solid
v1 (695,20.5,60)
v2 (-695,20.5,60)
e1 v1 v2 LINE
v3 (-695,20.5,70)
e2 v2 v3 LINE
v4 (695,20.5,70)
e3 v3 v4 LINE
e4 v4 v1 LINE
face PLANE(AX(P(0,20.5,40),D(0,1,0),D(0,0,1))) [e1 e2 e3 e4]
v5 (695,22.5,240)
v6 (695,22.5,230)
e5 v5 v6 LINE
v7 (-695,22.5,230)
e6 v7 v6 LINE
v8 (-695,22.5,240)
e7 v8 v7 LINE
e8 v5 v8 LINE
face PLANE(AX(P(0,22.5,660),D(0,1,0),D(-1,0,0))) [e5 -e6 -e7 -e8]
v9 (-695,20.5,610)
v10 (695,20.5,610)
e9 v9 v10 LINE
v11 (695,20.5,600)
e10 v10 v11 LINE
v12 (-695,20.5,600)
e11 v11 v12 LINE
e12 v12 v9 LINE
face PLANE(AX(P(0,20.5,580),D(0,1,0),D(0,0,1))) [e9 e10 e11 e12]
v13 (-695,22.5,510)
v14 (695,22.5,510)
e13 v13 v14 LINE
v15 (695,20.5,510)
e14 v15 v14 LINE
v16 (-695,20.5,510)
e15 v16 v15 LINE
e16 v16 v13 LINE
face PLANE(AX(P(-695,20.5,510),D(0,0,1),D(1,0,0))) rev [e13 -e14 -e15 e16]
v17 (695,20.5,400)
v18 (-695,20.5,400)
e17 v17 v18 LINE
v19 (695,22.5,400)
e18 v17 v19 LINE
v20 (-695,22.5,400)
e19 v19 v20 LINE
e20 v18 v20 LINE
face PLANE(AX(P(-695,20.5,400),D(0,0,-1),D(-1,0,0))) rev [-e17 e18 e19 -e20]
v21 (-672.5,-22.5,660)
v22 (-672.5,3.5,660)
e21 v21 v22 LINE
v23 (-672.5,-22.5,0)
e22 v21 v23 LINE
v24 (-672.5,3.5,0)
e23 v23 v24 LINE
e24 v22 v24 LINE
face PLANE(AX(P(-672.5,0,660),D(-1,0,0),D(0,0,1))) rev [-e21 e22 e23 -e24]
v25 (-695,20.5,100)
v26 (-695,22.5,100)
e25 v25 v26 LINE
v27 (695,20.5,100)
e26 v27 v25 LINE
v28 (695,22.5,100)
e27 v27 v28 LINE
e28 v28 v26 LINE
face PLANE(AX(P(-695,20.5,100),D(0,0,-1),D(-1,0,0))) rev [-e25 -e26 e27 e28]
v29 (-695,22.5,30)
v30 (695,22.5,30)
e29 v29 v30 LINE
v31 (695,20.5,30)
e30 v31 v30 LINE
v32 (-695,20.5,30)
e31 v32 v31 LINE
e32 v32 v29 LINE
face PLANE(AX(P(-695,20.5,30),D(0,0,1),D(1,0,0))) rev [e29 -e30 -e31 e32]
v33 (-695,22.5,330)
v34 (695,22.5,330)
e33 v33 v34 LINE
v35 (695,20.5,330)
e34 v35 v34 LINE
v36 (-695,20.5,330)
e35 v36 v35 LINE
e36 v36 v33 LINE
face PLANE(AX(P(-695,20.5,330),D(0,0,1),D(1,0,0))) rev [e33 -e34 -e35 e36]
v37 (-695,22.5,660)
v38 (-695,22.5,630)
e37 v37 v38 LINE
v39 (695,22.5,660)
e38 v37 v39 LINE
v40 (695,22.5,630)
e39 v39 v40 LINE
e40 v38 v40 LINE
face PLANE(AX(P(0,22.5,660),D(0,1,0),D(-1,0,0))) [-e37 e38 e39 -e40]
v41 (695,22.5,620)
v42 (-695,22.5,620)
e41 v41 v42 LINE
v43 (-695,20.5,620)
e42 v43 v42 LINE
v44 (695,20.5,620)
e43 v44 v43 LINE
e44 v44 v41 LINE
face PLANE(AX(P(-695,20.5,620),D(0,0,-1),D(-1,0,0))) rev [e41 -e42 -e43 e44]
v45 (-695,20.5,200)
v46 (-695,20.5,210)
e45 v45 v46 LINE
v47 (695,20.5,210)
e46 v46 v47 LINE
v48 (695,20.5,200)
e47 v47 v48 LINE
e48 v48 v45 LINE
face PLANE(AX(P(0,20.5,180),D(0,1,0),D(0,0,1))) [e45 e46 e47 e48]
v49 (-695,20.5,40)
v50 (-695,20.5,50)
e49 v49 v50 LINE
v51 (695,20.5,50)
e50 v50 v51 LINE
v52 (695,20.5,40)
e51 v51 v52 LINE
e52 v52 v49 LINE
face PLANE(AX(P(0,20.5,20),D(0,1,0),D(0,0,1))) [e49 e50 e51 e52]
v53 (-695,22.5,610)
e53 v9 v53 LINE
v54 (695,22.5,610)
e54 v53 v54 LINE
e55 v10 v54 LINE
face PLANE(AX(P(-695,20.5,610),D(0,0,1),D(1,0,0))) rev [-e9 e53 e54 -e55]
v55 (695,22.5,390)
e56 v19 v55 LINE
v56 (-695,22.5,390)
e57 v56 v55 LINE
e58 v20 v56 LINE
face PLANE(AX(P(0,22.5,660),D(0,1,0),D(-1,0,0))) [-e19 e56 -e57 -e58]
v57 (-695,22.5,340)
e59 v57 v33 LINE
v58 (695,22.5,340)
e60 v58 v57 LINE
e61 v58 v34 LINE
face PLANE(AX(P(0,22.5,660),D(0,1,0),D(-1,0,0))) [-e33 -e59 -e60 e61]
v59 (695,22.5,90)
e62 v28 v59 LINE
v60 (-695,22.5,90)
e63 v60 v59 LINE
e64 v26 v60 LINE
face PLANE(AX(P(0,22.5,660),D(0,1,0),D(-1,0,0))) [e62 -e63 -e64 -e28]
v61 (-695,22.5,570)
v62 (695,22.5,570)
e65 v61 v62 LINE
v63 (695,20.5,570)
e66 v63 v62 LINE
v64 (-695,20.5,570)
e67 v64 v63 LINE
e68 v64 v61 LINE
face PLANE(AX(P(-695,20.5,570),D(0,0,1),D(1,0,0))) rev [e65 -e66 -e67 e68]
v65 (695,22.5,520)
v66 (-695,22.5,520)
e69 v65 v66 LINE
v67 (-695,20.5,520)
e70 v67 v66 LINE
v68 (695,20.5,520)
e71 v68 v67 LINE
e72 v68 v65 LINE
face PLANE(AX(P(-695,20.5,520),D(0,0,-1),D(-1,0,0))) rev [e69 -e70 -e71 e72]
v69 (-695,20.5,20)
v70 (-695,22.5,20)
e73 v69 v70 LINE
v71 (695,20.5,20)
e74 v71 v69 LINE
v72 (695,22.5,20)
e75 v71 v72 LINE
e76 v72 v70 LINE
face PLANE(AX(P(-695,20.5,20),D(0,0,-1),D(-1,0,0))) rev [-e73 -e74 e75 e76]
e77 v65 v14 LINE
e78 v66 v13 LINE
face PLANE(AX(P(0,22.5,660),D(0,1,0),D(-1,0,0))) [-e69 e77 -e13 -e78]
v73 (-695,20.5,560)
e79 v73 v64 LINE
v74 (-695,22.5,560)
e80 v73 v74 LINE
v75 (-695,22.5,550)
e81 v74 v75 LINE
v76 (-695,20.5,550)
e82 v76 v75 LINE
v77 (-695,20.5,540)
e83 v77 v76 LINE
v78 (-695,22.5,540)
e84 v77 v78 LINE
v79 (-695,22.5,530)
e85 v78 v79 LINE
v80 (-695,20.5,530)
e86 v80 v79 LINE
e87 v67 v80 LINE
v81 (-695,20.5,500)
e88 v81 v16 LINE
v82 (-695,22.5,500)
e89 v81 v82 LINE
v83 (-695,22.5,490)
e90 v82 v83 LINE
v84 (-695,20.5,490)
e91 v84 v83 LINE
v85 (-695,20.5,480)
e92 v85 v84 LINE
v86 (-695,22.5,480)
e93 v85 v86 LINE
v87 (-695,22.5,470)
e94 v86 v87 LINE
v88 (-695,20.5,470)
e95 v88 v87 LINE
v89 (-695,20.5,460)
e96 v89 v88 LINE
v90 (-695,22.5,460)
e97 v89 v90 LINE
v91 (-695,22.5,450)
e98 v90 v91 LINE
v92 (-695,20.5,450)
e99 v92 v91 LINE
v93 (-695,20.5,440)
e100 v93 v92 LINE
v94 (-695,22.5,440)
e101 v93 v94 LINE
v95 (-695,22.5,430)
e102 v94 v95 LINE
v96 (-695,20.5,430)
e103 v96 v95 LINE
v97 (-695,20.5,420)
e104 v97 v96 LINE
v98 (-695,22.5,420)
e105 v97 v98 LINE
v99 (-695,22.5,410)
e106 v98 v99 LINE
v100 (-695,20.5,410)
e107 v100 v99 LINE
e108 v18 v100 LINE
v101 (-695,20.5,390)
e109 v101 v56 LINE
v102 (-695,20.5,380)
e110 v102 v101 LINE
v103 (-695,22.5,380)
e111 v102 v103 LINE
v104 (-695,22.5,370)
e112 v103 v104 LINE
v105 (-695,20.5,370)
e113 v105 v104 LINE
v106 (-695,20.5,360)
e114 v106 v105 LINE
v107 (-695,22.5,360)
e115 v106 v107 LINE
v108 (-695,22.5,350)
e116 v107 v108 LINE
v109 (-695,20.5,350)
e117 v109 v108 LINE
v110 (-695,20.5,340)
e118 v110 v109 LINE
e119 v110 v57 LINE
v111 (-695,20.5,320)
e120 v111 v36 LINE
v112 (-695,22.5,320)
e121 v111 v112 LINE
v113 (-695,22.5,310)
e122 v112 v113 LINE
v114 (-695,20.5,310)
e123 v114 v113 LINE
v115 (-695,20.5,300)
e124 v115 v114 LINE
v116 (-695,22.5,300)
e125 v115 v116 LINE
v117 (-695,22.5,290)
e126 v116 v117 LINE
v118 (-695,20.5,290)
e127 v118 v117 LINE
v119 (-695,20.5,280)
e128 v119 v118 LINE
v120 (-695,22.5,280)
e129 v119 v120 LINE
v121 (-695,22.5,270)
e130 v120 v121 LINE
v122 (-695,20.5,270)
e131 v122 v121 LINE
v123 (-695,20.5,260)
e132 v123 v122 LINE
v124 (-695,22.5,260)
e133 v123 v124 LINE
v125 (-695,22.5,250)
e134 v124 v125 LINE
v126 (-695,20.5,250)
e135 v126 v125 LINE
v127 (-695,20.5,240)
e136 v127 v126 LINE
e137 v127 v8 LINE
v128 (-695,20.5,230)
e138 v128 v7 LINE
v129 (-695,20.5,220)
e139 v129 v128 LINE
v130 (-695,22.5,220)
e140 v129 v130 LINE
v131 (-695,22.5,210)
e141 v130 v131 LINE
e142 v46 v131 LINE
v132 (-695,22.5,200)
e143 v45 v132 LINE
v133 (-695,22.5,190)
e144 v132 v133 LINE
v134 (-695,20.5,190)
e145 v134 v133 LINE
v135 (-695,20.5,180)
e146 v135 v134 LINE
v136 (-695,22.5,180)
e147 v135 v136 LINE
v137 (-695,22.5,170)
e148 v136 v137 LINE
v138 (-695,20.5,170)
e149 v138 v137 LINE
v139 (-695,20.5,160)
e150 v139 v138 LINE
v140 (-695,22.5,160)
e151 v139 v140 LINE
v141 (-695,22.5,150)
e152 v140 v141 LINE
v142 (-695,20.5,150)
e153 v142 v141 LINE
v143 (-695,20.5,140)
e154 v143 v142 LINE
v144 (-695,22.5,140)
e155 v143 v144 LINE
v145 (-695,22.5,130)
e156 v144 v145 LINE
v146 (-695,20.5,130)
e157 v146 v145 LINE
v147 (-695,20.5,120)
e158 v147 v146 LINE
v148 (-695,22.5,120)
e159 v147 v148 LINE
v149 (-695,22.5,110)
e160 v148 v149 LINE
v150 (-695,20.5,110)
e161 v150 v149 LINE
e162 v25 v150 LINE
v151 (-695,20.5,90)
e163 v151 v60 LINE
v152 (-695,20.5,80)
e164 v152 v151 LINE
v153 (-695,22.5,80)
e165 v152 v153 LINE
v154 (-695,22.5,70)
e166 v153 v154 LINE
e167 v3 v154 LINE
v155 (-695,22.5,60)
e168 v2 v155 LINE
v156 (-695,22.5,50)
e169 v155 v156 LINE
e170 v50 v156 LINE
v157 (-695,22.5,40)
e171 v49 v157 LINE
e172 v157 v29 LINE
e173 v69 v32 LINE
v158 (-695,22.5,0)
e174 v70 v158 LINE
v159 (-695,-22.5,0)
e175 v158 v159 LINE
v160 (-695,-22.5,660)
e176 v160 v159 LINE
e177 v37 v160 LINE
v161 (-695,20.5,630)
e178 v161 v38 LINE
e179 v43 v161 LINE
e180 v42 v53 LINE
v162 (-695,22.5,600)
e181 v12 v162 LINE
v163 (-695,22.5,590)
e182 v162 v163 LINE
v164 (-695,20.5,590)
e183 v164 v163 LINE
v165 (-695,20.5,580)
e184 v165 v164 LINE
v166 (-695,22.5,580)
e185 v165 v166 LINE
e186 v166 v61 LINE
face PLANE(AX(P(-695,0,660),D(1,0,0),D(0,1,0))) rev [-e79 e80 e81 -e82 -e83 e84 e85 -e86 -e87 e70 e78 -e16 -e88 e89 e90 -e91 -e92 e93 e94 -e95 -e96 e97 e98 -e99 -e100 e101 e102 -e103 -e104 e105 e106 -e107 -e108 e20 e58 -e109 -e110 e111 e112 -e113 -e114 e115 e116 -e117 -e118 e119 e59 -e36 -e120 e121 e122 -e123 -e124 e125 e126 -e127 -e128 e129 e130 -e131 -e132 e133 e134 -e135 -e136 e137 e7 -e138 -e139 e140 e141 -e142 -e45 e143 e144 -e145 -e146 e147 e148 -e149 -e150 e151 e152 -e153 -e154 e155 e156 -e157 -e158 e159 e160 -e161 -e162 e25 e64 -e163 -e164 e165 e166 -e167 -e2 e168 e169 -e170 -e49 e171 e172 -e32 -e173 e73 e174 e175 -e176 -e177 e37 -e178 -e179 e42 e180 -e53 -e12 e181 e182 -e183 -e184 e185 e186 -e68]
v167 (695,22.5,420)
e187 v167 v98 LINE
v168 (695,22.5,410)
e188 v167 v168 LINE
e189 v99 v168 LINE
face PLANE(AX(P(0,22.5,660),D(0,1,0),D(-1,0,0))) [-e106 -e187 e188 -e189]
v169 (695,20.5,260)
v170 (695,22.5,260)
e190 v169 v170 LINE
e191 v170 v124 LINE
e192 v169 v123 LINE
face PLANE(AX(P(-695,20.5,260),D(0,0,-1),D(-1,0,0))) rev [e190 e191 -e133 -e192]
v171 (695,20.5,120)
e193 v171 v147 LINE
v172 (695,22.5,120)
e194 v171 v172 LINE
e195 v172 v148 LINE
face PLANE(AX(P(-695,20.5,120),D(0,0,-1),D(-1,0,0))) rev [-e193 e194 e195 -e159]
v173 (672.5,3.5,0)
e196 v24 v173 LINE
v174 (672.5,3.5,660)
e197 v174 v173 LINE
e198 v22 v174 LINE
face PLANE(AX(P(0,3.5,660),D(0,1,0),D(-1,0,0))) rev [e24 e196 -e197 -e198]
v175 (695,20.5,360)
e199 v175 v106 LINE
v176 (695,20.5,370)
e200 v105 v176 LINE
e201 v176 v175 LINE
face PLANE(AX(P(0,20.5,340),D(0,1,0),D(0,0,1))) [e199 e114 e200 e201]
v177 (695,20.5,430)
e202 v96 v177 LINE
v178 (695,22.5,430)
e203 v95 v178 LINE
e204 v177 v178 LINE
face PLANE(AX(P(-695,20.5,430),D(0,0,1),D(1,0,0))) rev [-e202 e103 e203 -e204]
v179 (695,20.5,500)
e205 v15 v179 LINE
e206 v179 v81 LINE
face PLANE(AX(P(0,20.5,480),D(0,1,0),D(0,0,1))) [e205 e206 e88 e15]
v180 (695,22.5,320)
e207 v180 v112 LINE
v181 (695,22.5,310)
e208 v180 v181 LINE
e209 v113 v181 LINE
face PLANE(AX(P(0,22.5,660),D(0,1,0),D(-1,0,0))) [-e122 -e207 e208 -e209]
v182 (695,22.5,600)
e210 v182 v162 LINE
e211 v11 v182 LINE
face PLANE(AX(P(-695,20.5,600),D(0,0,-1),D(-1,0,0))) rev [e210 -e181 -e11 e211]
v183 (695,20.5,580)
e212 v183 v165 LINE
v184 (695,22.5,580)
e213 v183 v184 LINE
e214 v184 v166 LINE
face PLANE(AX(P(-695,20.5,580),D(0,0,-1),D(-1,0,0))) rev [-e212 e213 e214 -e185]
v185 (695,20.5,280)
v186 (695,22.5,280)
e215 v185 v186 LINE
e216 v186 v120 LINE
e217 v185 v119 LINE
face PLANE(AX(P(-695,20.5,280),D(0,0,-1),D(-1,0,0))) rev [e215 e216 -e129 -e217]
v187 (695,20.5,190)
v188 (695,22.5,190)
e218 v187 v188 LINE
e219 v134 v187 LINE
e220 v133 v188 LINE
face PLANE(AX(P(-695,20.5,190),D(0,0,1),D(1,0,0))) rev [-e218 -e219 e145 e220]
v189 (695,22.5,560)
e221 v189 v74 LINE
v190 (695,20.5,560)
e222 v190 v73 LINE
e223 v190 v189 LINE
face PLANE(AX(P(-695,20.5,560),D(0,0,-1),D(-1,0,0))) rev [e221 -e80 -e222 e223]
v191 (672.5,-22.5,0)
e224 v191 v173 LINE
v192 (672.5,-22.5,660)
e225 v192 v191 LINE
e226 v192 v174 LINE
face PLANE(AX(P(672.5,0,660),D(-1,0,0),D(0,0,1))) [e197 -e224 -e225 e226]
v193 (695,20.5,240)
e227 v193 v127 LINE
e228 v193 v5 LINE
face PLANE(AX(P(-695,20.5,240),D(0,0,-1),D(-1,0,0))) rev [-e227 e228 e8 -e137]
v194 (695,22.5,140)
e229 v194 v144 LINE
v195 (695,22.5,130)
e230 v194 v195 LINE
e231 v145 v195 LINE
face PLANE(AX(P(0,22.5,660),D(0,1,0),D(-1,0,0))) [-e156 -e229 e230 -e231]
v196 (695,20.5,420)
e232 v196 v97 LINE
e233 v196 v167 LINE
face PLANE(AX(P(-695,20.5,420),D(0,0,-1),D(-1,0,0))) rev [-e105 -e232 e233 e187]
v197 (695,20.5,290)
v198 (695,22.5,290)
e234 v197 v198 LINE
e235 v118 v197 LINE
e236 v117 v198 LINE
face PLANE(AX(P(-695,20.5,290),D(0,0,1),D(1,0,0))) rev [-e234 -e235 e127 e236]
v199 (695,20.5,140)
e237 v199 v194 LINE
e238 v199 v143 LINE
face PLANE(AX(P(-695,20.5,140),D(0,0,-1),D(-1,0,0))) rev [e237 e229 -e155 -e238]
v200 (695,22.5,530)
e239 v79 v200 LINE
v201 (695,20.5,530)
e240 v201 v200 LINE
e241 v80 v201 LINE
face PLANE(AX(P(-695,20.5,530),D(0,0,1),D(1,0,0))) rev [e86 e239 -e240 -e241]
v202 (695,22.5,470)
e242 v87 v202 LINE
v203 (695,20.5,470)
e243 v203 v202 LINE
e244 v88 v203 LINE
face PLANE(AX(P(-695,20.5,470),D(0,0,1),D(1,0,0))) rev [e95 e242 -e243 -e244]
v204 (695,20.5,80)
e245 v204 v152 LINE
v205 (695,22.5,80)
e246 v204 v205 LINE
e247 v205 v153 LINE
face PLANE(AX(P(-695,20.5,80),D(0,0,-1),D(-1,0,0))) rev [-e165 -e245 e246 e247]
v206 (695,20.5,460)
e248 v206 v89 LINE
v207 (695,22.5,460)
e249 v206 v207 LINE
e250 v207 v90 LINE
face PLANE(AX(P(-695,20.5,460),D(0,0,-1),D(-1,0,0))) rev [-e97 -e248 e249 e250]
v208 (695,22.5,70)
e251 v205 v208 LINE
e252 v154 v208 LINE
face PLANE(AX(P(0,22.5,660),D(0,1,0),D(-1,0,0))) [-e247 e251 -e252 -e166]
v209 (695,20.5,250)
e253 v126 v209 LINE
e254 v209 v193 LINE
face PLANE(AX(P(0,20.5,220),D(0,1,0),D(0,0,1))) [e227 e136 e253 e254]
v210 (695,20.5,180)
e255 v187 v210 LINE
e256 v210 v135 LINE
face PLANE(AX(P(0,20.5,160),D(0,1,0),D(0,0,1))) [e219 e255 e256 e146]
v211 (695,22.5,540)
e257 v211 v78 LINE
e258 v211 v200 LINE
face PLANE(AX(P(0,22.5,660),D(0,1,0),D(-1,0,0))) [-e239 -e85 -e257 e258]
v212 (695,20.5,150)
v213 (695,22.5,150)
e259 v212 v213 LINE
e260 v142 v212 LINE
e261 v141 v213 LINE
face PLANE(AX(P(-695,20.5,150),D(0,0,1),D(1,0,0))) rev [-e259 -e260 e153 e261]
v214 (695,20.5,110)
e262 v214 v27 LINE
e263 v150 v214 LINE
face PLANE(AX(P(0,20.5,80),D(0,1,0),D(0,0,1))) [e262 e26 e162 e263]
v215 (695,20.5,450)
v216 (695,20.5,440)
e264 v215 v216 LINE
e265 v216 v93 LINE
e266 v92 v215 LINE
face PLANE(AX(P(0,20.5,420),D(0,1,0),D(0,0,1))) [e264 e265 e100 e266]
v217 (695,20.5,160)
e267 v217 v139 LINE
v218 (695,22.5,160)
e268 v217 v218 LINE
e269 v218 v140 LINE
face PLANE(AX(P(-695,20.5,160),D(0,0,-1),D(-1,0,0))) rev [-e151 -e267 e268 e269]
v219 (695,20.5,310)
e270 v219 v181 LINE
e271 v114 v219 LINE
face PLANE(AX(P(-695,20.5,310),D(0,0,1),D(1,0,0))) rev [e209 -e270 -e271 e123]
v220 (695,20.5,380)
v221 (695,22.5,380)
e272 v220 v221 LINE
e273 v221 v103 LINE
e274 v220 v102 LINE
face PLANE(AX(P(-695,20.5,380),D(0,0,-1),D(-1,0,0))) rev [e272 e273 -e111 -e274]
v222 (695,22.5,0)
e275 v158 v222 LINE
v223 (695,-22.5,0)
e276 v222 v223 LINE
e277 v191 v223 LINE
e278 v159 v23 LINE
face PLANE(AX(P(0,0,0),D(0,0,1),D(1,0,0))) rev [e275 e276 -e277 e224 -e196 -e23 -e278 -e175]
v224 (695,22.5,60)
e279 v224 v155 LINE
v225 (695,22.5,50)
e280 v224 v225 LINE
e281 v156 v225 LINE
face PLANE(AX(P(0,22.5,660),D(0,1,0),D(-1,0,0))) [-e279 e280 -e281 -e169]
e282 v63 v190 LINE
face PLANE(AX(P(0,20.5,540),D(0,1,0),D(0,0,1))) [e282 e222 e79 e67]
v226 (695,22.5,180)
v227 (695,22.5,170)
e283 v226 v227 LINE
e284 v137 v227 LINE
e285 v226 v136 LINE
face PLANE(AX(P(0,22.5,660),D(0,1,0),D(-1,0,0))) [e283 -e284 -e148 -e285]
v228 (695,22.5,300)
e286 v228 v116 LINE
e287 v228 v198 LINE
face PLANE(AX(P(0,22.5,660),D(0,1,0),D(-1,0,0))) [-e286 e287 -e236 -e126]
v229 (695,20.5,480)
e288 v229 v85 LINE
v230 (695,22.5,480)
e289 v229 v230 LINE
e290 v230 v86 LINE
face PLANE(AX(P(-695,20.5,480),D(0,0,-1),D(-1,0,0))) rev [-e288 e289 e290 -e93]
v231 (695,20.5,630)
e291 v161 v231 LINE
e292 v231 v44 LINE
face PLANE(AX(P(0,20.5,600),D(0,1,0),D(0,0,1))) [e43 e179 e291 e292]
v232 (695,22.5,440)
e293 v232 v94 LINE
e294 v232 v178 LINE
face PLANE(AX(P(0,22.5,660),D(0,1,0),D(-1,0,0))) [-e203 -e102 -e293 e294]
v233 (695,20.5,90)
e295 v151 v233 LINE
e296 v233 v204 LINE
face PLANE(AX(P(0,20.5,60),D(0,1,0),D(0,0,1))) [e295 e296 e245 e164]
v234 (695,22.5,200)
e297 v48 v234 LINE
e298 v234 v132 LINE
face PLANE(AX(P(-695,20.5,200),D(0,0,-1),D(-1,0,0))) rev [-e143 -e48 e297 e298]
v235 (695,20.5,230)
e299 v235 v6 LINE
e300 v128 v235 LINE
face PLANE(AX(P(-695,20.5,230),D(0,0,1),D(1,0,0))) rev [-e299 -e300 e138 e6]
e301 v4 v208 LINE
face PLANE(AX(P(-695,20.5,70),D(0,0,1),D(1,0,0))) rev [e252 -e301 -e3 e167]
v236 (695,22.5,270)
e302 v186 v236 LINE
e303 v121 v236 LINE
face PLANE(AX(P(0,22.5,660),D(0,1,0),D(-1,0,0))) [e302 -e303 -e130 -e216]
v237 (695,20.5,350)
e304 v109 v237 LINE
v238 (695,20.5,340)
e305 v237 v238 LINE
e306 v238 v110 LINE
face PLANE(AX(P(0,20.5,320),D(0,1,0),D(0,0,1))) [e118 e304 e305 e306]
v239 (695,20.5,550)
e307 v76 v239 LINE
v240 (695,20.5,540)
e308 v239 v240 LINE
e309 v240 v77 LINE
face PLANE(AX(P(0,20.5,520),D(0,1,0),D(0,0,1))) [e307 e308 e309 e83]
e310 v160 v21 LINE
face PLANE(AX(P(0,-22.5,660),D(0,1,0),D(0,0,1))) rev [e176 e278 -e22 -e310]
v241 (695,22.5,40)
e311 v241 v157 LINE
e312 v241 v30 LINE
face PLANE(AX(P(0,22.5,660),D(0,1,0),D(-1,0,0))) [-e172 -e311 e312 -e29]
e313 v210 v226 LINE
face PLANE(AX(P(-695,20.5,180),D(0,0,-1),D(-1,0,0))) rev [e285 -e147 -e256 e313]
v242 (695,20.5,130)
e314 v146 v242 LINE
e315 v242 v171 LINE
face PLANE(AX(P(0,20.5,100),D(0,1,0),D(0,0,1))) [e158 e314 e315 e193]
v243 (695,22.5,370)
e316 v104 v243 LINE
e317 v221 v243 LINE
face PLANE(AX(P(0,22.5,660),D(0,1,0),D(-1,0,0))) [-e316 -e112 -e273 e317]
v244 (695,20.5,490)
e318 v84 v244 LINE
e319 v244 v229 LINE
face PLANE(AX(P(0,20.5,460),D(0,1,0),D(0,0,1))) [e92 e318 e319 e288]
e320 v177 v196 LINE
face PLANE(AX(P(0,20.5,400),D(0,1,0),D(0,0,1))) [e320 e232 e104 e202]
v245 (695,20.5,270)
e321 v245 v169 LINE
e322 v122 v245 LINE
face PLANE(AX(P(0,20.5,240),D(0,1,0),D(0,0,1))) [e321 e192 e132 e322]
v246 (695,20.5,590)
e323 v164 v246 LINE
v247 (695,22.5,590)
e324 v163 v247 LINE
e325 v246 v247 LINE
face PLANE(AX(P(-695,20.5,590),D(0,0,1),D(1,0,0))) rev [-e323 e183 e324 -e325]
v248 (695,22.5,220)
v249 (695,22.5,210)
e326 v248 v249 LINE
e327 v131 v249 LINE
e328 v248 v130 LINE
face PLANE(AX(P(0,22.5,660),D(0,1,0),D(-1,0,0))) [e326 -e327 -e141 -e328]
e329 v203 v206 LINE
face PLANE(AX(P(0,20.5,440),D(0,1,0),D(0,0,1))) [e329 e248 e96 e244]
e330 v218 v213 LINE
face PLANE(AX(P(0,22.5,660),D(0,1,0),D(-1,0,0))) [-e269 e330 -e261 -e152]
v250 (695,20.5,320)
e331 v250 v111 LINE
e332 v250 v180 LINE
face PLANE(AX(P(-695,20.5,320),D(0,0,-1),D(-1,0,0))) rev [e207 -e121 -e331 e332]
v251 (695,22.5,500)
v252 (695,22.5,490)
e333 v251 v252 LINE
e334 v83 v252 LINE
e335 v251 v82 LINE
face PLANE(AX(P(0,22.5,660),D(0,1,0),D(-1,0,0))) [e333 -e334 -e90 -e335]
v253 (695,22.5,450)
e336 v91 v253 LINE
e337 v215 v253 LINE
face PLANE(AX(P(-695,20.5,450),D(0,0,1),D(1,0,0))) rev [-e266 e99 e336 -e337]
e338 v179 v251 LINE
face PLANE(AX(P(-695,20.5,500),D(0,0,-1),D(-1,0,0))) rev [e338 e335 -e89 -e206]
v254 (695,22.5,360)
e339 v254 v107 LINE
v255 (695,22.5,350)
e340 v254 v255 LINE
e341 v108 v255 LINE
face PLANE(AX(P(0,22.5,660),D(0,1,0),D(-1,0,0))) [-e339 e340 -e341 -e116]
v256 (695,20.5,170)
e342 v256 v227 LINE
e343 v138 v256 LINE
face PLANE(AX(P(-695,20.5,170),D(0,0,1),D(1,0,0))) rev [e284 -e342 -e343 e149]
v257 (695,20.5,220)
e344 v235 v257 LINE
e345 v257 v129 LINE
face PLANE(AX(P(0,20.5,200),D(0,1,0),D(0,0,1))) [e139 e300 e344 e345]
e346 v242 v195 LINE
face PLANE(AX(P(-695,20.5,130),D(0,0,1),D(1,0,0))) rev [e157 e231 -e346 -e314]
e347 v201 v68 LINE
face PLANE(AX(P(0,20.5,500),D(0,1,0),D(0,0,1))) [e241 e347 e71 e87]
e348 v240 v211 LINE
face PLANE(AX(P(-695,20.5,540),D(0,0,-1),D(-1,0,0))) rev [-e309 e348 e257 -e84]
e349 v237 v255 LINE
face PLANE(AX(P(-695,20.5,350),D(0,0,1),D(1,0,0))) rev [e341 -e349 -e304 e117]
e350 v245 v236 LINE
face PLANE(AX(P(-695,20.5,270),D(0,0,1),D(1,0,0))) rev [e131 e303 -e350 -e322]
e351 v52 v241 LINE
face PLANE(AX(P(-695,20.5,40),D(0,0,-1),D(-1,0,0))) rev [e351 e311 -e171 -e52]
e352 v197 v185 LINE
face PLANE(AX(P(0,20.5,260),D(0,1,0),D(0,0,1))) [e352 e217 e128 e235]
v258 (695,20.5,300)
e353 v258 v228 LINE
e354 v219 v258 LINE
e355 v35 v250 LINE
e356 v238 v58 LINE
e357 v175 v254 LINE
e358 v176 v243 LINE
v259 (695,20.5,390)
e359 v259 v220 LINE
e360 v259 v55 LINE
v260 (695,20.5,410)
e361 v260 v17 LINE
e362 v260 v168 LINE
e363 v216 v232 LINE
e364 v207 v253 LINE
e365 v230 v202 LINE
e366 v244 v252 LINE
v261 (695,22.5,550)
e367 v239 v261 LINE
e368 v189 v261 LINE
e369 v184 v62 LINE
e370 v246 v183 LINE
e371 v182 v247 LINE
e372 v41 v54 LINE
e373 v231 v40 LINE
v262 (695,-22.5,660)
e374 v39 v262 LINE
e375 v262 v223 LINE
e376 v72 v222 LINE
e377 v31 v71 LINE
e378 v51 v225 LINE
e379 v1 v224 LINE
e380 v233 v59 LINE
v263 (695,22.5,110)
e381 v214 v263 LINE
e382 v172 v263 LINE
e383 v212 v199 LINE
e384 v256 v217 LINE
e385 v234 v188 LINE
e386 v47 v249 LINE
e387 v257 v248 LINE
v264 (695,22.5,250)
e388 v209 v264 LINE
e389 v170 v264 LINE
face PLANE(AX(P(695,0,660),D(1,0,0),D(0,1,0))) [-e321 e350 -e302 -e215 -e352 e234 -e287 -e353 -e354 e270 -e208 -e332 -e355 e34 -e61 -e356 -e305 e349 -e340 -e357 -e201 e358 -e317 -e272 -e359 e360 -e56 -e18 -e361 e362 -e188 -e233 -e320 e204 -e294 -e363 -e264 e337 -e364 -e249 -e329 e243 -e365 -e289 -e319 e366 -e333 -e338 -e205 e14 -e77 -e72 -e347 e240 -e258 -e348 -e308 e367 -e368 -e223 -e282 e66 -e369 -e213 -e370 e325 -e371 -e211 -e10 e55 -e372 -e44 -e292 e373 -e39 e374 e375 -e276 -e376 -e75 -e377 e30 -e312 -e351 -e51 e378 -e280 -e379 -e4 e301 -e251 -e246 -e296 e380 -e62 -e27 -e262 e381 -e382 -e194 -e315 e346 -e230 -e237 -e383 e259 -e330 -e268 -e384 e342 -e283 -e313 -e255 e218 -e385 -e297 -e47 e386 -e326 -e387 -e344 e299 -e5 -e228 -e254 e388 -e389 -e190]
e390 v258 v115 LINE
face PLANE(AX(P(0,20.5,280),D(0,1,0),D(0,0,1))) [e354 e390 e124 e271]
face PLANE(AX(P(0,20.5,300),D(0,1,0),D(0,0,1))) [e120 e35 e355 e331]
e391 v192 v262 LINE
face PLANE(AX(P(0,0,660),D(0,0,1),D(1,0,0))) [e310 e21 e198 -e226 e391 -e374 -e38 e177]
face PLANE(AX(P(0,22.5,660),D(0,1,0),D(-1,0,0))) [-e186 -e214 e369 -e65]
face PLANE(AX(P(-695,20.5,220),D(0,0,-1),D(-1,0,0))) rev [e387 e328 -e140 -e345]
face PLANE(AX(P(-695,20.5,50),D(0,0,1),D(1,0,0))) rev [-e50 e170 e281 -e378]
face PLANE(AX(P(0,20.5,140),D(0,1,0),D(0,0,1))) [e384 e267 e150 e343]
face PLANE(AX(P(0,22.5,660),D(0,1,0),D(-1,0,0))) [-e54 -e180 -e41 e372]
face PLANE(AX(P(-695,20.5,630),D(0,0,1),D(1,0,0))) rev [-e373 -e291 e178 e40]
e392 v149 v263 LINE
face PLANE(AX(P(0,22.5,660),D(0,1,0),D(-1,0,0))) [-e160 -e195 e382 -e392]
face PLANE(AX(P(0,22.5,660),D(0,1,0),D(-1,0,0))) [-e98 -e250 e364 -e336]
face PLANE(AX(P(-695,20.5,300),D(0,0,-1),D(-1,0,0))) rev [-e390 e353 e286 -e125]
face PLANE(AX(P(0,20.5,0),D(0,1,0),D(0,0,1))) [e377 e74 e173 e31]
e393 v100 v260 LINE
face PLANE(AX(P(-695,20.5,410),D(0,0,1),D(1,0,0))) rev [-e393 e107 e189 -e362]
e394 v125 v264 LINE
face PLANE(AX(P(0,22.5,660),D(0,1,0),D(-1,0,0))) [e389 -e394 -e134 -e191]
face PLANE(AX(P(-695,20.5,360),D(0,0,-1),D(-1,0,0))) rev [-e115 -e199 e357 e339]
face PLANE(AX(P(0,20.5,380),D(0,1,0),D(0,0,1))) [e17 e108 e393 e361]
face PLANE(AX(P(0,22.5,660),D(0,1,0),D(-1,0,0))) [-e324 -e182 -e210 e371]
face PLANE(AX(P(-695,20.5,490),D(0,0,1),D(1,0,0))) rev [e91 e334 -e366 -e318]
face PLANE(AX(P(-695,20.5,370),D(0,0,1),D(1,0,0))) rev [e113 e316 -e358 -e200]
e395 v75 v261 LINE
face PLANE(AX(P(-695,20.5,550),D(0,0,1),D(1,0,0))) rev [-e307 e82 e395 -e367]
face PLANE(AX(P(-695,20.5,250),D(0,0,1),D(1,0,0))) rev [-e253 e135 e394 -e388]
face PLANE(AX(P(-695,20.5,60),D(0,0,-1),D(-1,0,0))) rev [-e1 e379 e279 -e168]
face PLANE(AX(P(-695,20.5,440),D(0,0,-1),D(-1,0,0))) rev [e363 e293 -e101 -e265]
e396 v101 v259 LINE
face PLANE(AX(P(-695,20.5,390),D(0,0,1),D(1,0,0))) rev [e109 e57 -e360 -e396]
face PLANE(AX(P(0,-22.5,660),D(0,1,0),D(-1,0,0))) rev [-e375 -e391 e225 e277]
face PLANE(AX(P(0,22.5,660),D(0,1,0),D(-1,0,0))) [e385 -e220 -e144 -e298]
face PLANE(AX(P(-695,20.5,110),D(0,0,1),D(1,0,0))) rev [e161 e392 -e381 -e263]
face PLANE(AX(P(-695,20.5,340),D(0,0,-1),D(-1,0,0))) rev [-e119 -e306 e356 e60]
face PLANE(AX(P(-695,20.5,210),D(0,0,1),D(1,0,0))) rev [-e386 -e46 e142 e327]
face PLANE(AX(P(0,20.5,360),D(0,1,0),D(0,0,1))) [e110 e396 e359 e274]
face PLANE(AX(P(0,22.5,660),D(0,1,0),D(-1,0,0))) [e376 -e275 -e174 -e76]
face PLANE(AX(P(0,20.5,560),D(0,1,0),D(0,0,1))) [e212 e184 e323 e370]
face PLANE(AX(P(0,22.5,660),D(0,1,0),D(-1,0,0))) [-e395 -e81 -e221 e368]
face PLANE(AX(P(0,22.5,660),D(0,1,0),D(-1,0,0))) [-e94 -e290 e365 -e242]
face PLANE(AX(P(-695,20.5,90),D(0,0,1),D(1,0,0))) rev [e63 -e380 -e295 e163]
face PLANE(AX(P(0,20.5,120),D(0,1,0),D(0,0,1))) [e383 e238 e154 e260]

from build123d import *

# Parameters (mm, degrees)
BOSS_EXTRUDE1_DEPTH = 660
SKETCH2_W           = 1390
SKETCH2_H           = 10
CUT_EXTRUDE1_DEPTH  = 2
LPATTERN1_COUNT     = 31
LPATTERN1_PITCH     = 20


with BuildPart() as part:
    # Sketch1 → Boss-Extrude1 (new body)
    with BuildSketch(Plane.XY):
        Polygon((0, 3.5), (0, 22.5), (-695, 22.5), (-695, -22.5), (-672.5, -22.5), (-672.5, 3.5), align=None)
        Polygon((695, 22.5), (0, 22.5), (0, 3.5), (672.5, 3.5), (672.5, -22.5), (695, -22.5), align=None)
    extrude(amount=BOSS_EXTRUDE1_DEPTH)

    # Sketch2 → Cut-Extrude1 (cut)
    with BuildSketch(Plane(origin=(0, 22.5, 0), x_dir=(1, 0, 0), z_dir=(0, 1, 0))):
        with Locations((0, -25)):
            Rectangle(SKETCH2_W, SKETCH2_H)
    cut_extrude1 = extrude(amount=-CUT_EXTRUDE1_DEPTH, mode=Mode.SUBTRACT)

    # LPattern1: Cut-Extrude1 ×31
    with Locations(*[(0, 0, i * LPATTERN1_PITCH) for i in range(1, LPATTERN1_COUNT)]):
        add(cut_extrude1, mode=Mode.SUBTRACT)


solid = part.part
